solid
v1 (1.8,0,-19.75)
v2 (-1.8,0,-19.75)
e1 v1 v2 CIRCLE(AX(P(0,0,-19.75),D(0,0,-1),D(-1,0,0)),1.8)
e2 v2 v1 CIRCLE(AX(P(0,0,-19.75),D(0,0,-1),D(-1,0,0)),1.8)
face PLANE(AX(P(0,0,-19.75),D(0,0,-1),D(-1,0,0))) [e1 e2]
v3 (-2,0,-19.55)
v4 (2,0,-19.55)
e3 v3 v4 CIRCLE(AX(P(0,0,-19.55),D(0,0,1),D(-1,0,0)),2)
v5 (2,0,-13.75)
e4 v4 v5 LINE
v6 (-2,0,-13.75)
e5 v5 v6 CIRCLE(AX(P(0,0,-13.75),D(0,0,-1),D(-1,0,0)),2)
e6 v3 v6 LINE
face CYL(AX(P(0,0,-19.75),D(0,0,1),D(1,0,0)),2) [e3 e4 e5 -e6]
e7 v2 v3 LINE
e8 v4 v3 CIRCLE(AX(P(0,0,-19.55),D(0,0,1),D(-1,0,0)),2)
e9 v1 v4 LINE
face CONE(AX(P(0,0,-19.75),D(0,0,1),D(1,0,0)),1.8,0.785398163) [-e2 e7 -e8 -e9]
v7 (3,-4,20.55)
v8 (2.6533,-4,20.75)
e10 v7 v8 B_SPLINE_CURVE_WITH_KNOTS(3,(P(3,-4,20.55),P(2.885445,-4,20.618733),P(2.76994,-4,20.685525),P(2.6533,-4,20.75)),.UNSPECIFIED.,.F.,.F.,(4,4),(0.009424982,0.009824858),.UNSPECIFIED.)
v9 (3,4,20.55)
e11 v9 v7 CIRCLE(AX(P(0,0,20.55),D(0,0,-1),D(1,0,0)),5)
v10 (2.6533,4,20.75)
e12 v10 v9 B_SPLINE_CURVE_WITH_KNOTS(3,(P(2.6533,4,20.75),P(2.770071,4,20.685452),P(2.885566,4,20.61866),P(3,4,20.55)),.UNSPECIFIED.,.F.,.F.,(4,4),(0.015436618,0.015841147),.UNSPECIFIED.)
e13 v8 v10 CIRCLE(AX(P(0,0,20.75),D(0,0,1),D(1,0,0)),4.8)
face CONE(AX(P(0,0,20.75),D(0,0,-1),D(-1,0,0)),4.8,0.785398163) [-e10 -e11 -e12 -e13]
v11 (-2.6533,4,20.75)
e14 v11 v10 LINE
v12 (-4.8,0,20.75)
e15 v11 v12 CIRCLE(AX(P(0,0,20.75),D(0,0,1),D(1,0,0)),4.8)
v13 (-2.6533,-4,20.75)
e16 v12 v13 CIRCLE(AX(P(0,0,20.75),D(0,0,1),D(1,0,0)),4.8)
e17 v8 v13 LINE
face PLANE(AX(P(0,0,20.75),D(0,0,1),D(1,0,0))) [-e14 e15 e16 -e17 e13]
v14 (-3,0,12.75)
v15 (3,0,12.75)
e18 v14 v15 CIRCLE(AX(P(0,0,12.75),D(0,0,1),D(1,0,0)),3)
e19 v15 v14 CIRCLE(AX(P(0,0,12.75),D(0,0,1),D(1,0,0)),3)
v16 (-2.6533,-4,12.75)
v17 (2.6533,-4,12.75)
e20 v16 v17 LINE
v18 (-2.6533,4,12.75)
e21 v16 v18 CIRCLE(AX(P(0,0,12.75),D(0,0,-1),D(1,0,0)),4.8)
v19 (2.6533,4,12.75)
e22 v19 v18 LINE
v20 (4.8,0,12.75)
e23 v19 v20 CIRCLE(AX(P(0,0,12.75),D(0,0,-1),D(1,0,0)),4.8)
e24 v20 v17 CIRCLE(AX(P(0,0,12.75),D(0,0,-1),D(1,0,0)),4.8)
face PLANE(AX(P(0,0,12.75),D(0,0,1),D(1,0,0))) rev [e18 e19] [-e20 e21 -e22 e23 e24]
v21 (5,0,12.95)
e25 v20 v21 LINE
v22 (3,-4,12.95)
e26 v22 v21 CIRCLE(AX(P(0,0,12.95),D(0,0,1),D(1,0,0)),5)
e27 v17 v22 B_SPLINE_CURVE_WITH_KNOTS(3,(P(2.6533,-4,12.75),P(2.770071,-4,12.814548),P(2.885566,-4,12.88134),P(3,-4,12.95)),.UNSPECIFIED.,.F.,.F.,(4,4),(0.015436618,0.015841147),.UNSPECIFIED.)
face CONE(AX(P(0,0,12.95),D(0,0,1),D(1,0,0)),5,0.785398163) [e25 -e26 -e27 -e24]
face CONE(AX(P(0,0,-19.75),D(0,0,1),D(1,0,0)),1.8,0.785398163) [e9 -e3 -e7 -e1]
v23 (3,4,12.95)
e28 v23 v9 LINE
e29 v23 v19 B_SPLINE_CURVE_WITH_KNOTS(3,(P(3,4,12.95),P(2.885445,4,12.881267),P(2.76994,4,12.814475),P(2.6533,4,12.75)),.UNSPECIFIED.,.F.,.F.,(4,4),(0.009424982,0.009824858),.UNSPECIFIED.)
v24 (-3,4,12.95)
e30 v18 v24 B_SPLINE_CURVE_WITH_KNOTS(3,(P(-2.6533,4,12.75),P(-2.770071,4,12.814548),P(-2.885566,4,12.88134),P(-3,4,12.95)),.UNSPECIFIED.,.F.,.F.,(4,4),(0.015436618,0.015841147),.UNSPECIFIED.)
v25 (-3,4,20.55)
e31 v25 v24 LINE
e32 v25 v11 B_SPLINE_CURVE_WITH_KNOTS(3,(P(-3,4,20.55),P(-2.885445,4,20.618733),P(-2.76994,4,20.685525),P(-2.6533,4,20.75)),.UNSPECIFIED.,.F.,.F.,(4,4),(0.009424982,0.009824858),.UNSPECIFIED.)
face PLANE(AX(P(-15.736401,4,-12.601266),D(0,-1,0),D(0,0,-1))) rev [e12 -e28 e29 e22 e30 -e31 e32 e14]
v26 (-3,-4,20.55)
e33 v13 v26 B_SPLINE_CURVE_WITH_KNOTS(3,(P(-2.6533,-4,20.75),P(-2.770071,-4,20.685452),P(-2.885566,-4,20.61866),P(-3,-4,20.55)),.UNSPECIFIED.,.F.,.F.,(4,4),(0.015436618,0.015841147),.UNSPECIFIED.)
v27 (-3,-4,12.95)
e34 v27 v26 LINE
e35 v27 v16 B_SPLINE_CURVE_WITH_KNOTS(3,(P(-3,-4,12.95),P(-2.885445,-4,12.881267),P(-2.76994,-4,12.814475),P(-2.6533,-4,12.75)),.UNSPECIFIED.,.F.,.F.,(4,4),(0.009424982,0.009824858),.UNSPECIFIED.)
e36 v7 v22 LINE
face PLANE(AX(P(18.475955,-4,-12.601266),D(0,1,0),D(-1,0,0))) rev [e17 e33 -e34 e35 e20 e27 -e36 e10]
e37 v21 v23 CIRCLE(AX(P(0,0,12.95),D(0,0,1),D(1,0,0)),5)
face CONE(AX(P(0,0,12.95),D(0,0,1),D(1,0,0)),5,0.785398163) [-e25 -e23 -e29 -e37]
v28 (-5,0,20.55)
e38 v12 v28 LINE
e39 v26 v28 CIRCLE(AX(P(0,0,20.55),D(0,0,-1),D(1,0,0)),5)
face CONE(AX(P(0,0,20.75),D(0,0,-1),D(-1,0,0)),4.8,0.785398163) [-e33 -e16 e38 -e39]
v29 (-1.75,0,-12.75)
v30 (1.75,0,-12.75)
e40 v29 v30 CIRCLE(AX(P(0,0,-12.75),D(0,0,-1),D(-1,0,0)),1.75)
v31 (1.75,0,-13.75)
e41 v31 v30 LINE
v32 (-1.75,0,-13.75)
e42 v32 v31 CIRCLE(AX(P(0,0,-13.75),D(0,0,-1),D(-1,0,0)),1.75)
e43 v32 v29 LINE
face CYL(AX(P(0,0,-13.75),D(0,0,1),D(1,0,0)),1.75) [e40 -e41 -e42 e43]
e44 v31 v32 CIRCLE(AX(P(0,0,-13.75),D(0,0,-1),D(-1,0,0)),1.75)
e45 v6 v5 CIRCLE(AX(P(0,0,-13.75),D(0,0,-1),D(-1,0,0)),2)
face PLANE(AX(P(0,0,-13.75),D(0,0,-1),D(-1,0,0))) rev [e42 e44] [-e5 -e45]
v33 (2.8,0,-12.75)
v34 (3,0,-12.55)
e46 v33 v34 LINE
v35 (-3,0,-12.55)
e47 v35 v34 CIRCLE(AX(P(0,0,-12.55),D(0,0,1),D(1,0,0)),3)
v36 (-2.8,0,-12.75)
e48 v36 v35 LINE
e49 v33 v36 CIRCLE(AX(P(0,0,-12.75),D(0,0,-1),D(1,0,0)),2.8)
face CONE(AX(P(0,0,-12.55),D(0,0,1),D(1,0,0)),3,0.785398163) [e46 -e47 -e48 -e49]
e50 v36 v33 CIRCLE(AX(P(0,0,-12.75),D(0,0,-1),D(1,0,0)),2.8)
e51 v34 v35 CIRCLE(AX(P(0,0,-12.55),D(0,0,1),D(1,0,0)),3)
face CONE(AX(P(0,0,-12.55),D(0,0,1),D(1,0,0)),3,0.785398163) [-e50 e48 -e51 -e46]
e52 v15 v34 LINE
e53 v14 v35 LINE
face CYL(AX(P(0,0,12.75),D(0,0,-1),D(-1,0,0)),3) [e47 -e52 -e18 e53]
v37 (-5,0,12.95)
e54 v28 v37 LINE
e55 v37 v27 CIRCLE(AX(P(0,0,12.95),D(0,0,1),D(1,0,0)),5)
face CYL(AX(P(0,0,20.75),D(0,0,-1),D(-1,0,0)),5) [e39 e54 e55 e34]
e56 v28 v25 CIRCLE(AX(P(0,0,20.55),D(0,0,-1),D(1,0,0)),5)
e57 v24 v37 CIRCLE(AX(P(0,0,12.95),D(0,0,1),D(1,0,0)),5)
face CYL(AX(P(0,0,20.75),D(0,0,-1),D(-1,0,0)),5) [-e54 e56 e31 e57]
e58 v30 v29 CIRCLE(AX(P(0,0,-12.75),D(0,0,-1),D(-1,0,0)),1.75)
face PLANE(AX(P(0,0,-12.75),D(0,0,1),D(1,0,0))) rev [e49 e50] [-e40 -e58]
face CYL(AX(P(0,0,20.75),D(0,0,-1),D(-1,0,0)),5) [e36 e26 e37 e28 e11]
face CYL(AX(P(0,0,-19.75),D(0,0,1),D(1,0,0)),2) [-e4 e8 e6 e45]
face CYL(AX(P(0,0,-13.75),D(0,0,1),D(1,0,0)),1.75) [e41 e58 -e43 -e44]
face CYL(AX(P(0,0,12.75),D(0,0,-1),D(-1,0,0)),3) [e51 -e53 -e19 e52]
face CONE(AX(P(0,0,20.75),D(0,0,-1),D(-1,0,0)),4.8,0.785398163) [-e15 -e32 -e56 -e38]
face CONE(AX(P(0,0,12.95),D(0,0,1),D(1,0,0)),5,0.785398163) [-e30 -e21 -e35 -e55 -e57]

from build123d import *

# Parameters (mm, degrees)
SKETCH_1_R          = 3
EXTRUDE_1_DEPTH     = 12.75
CHAMFER_1_SIZE      = 0.2
SKETCH_2_R          = 2
EXTRUDE_2_DEPTH     = 7
CHAMFER_2_SIZE      = 0.2
SKETCH_3_R          = 5
EXTRUDE_3_DEPTH     = 8
CHAMFER_3_SIZE      = 0.2
CUT_EXTRUDE_1_REACH = 43.113
SKETCH_4_W          = 22.304994934
SKETCH_4_H          = 6.13630865
SKETCH_4_W_2        = 24.691337186
SKETCH_4_H_2        = 5.746701752
SKETCH_5_OUTSIDE_W  = 20.496
SKETCH_5_OUTSIDE_H  = 18.496
SKETCH_5_OUTSIDE_R  = 1.75
CUT_EXTRUDE_2_DEPTH = 1


with BuildPart() as part:
    # 草图1 → 凸台-拉伸1 (new, symmetric)
    with BuildSketch(Plane.XY):
        Circle(SKETCH_1_R)
    extrude(amount=EXTRUDE_1_DEPTH, both=True)

    # 倒角1
    chamfer_1_edges = [part.edges().sort_by_distance(p)[0] for p in [
        (-3, 0, -12.75),
    ]]
    chamfer(chamfer_1_edges, length=CHAMFER_1_SIZE)

    # 草图2 → 凸台-拉伸2 (add)
    with BuildSketch(Plane(origin=(0, 0, -12.75), x_dir=(-1, 0, 0), z_dir=(0, 0, -1))):
        with Locations(Location((0, 0, 0), (0, 0, 180))):
            Circle(SKETCH_2_R)
    extrude(amount=EXTRUDE_2_DEPTH)

    # 倒角2
    chamfer_2_edges = [part.edges().sort_by_distance(p)[0] for p in [
        (-2, 0, -19.75),
    ]]
    chamfer(chamfer_2_edges, length=CHAMFER_2_SIZE)

    # 草图3 → 凸台-拉伸3 (add)
    with BuildSketch(Plane.XY.offset(12.75)):
        Circle(SKETCH_3_R)
    extrude(amount=EXTRUDE_3_DEPTH)

    # 倒角3
    chamfer_3_edges = [part.edges().sort_by_distance(p)[0] for p in [
        (-5, 0, 12.75),
        (-5, 0, 20.75),
    ]]
    chamfer(chamfer_3_edges, length=CHAMFER_3_SIZE)

    # 切除-拉伸1: up to this face of the body (flat: up to its plane)
    cut_extrude_1_end = Plane(part.part.faces().sort_by_distance((-4.664235498, 0, 12.75))[0])
    # 草图4 → 切除-拉伸1 (cut, up to the picked face)
    with BuildSketch(Plane.XY.offset(20.75), mode=Mode.PRIVATE) as cut_extrude_1_sk1:
        with Locations((-4.583903449, 7.068154325)):
            Rectangle(SKETCH_4_W, SKETCH_4_H)
    cut_extrude_1_tool1 = split(extrude(cut_extrude_1_sk1.sketch, amount=-CUT_EXTRUDE_1_REACH, mode=Mode.PRIVATE), bisect_by=cut_extrude_1_end, keep=Keep.BOTH, mode=Mode.PRIVATE)
    # 草图4 → 切除-拉伸1 (cut, up to the picked face)
    with BuildSketch(Plane.XY.offset(20.75), mode=Mode.PRIVATE) as cut_extrude_1_sk2:
        with Locations((6.130286257, -6.873350876)):
            Rectangle(SKETCH_4_W_2, SKETCH_4_H_2)
    cut_extrude_1_tool2 = split(extrude(cut_extrude_1_sk2.sketch, amount=-CUT_EXTRUDE_1_REACH, mode=Mode.PRIVATE), bisect_by=cut_extrude_1_end, keep=Keep.BOTH, mode=Mode.PRIVATE)
    add(cut_extrude_1_tool1.solids().sort_by(Axis((-4.583903, 7.068154, 20.75), (0, 0, -1)))[0], mode=Mode.SUBTRACT)
    add(cut_extrude_1_tool2.solids().sort_by(Axis((6.130286, -6.873351, 20.75), (0, 0, -1)))[0], mode=Mode.SUBTRACT)

    # 草图5 outside → 切除-拉伸2 (cut)
    with BuildSketch(Plane(origin=(0, 0, -12.75), x_dir=(-1, 0, 0), z_dir=(0, 0, -1))):
        Rectangle(SKETCH_5_OUTSIDE_W, SKETCH_5_OUTSIDE_H)
        Circle(SKETCH_5_OUTSIDE_R, mode=Mode.SUBTRACT)
    extrude(amount=CUT_EXTRUDE_2_DEPTH, mode=Mode.SUBTRACT)


solid = part.part
